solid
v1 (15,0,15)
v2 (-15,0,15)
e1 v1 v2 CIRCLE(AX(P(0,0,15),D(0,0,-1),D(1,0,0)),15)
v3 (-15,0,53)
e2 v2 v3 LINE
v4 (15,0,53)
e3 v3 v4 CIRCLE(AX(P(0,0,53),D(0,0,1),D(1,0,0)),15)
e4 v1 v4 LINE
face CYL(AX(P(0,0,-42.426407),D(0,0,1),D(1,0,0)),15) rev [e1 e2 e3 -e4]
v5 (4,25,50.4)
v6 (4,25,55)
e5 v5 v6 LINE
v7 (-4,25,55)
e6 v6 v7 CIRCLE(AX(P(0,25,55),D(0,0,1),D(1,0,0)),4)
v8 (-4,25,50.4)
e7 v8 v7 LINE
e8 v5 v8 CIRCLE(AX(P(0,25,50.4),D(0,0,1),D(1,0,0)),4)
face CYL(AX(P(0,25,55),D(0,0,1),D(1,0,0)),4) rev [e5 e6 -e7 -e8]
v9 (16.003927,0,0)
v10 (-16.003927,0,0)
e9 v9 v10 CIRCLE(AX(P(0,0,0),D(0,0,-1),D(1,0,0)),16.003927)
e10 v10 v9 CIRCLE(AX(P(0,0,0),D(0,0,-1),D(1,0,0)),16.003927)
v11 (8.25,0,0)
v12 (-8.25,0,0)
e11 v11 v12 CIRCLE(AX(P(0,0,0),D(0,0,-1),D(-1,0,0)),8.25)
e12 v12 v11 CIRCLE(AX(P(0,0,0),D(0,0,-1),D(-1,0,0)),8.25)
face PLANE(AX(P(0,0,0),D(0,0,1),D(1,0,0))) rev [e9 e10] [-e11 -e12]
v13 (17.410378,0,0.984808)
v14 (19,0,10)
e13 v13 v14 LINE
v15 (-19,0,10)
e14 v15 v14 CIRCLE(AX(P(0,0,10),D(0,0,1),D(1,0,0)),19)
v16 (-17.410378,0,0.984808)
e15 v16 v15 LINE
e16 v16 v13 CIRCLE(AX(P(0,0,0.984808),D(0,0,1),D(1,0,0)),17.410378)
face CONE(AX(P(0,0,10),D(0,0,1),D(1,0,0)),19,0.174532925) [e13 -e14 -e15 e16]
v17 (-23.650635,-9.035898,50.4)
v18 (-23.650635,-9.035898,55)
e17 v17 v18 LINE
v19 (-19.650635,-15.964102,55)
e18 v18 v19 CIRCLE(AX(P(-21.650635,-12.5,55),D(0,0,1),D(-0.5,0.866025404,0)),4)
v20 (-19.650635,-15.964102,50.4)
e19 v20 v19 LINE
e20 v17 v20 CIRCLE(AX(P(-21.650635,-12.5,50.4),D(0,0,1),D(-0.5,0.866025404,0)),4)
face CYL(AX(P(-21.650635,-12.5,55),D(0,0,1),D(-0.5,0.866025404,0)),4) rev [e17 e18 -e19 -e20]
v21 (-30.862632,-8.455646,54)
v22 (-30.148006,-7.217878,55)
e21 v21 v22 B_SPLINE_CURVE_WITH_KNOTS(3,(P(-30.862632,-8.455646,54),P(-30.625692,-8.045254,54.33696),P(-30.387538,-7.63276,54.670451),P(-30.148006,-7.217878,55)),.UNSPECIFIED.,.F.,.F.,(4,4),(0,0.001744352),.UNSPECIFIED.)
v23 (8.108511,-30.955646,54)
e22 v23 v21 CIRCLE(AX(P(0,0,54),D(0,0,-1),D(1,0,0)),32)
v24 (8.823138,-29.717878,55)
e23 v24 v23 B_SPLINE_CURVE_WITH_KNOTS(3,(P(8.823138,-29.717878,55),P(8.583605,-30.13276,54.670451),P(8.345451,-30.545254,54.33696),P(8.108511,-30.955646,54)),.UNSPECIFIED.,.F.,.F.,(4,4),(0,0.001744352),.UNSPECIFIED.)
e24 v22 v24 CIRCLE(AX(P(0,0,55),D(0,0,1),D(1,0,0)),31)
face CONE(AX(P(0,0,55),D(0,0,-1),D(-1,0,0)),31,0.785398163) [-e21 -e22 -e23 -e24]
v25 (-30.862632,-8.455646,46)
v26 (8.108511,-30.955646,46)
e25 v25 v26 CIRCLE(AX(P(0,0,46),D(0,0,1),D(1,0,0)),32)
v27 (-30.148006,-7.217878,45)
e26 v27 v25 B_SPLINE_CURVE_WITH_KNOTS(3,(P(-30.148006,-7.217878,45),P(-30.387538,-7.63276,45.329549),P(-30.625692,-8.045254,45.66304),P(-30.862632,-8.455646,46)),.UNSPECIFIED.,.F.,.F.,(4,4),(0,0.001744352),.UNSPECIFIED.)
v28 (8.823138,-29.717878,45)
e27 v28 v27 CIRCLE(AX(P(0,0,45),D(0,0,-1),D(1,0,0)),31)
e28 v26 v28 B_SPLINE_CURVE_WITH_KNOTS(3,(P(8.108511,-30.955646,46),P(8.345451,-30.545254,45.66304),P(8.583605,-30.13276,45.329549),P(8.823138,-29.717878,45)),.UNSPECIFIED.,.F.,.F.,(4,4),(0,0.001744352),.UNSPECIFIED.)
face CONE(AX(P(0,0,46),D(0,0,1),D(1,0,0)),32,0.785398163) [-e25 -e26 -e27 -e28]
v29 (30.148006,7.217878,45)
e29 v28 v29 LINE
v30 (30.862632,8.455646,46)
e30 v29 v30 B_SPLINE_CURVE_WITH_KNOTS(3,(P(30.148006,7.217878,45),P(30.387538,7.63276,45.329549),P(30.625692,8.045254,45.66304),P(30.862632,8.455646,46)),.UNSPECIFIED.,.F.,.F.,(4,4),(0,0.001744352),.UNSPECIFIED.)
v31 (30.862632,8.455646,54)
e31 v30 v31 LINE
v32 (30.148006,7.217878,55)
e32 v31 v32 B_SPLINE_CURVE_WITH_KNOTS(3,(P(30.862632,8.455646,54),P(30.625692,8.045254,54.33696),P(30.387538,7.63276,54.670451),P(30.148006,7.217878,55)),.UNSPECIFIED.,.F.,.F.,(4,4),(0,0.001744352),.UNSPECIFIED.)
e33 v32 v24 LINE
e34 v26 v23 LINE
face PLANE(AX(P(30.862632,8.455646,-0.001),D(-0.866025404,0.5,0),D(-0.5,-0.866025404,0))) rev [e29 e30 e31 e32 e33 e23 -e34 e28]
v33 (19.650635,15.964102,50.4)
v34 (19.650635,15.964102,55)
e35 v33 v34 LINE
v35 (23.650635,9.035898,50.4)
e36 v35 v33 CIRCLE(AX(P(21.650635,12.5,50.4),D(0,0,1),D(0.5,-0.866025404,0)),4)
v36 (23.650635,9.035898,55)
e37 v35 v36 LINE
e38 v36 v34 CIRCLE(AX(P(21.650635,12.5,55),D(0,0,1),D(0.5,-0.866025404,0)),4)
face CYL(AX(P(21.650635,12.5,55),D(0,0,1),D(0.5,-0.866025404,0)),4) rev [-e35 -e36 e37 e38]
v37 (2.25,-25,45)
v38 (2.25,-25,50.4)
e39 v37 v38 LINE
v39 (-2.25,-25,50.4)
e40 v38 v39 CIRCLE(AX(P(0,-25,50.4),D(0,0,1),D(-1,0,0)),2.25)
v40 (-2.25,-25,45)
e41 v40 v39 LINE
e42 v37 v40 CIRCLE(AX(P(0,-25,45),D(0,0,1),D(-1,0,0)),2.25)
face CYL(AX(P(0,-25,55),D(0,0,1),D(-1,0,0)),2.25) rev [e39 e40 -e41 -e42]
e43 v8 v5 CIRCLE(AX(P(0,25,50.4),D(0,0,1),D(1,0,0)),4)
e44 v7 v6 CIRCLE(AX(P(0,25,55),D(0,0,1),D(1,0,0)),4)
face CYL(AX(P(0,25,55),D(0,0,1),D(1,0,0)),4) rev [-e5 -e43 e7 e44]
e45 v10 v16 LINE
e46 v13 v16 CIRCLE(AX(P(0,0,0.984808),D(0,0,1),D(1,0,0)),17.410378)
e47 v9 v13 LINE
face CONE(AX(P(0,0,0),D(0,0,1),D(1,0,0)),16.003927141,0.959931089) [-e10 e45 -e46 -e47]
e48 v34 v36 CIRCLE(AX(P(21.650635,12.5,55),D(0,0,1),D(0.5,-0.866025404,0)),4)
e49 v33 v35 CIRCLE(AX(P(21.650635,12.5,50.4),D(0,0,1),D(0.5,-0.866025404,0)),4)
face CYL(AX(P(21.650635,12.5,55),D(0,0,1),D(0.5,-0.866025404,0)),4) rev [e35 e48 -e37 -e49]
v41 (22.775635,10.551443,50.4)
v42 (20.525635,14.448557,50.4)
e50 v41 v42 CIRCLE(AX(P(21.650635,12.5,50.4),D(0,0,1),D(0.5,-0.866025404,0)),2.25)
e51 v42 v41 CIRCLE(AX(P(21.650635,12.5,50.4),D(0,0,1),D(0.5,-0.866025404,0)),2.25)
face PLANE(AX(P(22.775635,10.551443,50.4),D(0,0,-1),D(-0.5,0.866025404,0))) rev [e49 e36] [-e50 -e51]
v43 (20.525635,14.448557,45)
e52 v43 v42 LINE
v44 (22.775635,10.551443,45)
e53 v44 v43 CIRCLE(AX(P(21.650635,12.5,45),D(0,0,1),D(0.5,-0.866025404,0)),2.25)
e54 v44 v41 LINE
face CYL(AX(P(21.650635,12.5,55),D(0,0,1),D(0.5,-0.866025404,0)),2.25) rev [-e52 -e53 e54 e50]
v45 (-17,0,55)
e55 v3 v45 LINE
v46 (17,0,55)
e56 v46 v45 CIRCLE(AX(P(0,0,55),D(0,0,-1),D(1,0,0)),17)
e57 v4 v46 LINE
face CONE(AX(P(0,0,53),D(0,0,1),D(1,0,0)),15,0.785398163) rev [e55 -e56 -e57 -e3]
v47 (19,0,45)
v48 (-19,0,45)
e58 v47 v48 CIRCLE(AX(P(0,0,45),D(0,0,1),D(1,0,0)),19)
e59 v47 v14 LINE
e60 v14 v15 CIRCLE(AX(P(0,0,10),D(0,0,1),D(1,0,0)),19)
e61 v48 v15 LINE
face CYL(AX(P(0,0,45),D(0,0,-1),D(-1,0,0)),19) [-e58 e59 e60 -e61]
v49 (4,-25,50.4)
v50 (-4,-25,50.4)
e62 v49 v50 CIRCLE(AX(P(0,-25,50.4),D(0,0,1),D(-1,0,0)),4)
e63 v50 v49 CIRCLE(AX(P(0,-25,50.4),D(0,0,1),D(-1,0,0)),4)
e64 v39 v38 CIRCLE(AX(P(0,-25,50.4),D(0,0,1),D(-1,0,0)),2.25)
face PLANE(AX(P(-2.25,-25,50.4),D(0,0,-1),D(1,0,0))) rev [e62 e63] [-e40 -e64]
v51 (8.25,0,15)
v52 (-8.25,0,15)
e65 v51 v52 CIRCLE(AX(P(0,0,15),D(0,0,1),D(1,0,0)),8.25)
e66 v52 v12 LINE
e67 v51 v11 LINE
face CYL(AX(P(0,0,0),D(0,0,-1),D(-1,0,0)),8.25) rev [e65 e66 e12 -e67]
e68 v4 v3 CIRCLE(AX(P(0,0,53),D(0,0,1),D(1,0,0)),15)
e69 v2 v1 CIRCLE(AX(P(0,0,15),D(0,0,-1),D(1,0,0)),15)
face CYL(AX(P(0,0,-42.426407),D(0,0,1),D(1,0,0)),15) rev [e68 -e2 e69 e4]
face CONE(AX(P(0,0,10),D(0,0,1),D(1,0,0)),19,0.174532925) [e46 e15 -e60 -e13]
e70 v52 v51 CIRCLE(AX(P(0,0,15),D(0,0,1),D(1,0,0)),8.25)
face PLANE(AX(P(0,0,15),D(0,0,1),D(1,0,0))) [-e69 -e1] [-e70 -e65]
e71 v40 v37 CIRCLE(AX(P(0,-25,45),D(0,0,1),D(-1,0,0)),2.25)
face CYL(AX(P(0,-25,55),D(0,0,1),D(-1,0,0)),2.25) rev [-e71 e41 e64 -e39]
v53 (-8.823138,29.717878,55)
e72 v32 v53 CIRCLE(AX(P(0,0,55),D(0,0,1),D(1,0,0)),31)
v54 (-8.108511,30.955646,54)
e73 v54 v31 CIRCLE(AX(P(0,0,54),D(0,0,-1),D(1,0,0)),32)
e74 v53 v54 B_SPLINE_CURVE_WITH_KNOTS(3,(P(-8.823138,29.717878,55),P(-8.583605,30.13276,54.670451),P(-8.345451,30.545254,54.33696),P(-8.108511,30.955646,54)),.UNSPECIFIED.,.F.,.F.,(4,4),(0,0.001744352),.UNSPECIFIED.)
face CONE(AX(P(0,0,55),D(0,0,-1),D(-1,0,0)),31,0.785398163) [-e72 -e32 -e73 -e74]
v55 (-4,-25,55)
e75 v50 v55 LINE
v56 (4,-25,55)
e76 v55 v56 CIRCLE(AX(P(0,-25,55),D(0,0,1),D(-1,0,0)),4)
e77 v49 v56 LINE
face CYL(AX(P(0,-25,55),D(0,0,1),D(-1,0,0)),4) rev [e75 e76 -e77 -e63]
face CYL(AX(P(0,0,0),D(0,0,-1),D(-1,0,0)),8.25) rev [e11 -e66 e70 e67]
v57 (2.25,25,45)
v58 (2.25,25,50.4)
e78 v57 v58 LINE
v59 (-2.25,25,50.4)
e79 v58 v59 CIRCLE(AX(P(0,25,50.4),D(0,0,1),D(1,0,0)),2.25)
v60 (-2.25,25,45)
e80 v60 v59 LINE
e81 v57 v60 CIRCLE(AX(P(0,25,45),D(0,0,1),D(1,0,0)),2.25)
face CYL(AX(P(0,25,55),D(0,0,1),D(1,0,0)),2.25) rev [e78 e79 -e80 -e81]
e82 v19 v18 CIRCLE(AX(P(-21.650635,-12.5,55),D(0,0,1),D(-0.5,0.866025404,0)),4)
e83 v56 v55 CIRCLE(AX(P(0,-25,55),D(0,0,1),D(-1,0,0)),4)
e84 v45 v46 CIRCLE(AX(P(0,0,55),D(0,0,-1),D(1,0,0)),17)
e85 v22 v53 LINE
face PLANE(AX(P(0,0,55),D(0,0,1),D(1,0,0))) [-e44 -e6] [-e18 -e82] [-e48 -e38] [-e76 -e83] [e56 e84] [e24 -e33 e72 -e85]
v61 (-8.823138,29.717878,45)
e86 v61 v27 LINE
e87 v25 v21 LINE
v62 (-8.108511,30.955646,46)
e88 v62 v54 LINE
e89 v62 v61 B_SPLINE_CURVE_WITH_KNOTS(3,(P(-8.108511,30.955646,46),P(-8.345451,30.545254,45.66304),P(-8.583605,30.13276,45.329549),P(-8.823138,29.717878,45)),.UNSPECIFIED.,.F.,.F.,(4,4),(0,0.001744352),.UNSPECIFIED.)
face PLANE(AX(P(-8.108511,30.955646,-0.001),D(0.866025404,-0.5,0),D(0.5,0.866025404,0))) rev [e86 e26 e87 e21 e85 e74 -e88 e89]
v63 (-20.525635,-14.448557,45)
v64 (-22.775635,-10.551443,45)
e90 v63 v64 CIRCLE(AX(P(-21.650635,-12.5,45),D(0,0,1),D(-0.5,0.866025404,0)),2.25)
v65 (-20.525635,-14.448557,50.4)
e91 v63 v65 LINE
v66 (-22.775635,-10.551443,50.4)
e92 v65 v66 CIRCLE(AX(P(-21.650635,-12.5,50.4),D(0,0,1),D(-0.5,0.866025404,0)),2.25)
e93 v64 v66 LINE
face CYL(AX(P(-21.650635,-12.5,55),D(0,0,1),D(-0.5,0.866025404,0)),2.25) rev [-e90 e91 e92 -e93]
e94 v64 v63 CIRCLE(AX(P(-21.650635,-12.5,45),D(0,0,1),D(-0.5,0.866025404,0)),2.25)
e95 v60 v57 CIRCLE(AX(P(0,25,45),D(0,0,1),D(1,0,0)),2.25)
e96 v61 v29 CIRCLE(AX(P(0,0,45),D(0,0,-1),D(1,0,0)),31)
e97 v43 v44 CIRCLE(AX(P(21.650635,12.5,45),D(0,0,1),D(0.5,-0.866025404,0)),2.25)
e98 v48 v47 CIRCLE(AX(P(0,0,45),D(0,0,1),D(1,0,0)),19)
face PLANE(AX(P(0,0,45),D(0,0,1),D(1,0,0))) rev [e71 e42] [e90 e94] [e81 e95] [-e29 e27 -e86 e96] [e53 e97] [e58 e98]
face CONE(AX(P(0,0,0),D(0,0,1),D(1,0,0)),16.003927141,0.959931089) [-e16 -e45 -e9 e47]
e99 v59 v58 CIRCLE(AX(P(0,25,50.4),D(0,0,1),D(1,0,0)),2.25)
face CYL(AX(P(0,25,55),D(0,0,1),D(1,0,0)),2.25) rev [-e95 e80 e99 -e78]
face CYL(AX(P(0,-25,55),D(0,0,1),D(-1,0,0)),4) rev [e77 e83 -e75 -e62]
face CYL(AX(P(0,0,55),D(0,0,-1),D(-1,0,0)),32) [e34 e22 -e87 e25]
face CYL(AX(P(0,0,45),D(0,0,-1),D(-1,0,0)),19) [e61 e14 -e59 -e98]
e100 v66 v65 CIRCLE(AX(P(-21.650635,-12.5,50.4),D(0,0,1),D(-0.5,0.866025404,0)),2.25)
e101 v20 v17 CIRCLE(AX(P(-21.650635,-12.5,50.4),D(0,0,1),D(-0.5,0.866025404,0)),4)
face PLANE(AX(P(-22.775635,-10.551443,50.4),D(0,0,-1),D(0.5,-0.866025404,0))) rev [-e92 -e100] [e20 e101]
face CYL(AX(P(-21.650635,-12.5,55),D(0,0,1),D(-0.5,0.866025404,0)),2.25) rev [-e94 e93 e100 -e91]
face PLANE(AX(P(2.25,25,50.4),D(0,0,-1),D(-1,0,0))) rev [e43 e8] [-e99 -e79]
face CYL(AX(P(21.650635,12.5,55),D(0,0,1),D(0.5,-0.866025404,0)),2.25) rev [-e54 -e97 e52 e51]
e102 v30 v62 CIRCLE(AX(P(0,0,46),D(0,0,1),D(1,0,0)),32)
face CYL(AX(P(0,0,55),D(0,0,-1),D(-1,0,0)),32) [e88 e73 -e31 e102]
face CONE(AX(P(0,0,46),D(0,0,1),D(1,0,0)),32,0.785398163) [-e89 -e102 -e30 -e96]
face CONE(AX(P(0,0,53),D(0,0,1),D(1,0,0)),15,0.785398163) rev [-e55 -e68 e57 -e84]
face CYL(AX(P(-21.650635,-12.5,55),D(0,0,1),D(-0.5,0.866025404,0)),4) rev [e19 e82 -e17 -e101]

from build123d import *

# Parameters (mm, degrees)
SKETCH1_R                                            = 19
BOSS_EXTRUDE1_DEPTH                                  = 45
SKETCH2_R                                            = 15
CUT_EXTRUDE1_DEPTH                                   = 30
M18X1_5_TAPPED_HOLE1_D                               = 16.5
M18X1_5_TAPPED_HOLE1_DEPTH                           = 43.5
M18X1_5_TAPPED_HOLE1_TIP                             = 4.957100107
BOSS_EXTRUDE2_START                                  = 10
SKETCH5_R                                            = 32
SKETCH5_R_2                                          = 15
BOSS_EXTRUDE2_DEPTH                                  = 10
HOLE_SIZE_PER_SOCKET_HEAD_CAP_SCREW_TYPE_D           = 4.5
HOLE_SIZE_PER_SOCKET_HEAD_CAP_SCREW_TYPE_CBORE_D     = 8
HOLE_SIZE_PER_SOCKET_HEAD_CAP_SCREW_TYPE_CBORE_DEPTH = 4.6
CIRPATTERN1_COUNT                                    = 6
CUT_EXTRUDE2_REACH                                   = 73.225
CHAMFER1_SIZE                                        = 1
CHAMFER2_SIZE                                        = 10
CHAMFER2_SIZE2                                       = 1.763269807
CHAMFER3_SIZE                                        = 1
CHAMFER3_SIZE2                                       = 1.232803052
CHAMFER4_SIZE                                        = 2


with BuildPart() as part:
    # Sketch1 → Boss-Extrude1 (new body)
    with BuildSketch(Plane.XY):
        with Locations(Location((0, 0, 0), (0, 0, 180))):
            Circle(SKETCH1_R)
    extrude(amount=BOSS_EXTRUDE1_DEPTH)

    # Sketch2 → Cut-Extrude1 (cut)
    with BuildSketch(Plane.XY.offset(45)):
        Circle(SKETCH2_R)
    extrude(amount=-CUT_EXTRUDE1_DEPTH, mode=Mode.SUBTRACT)

    # M18x1.5 Tapped Hole1
    with Locations(Plane(origin=(0, 0, 0), x_dir=(-1, 0, 0), z_dir=(0, 0, -1))):
        with Locations((0, 0)):
            Hole(M18X1_5_TAPPED_HOLE1_D / 2, depth=M18X1_5_TAPPED_HOLE1_DEPTH)
            with Locations((0, 0, -(M18X1_5_TAPPED_HOLE1_DEPTH + M18X1_5_TAPPED_HOLE1_TIP / 2))):  # 118° drill point
                Cone(0, M18X1_5_TAPPED_HOLE1_D / 2, M18X1_5_TAPPED_HOLE1_TIP, mode=Mode.SUBTRACT)

    # Sketch5 → Boss-Extrude2 (add)
    with BuildSketch(Plane.XY.offset(45).offset(BOSS_EXTRUDE2_START)):
        Circle(SKETCH5_R)
        Circle(SKETCH5_R_2, mode=Mode.SUBTRACT)
    extrude(amount=-BOSS_EXTRUDE2_DEPTH)

    # Hole size per socket head cap screw type1 (through all)
    with Locations(Plane(origin=(0, 25, 55), x_dir=(1, 0, 0), z_dir=(0, 0, 1))):
        with Locations((0, 0)):
            hole_size_per_socket_head_cap_screw_type = CounterBoreHole(HOLE_SIZE_PER_SOCKET_HEAD_CAP_SCREW_TYPE_D / 2, HOLE_SIZE_PER_SOCKET_HEAD_CAP_SCREW_TYPE_CBORE_D / 2, HOLE_SIZE_PER_SOCKET_HEAD_CAP_SCREW_TYPE_CBORE_DEPTH)

    # CirPattern1: Hole size per socket head cap screw type1 ×6 about axis, 2 skipped
    cirpattern1_axis = Axis((0, 0, 55), (0, 0, 1))
    add([hole_size_per_socket_head_cap_screw_type.rotate(cirpattern1_axis, i * 360 / CIRPATTERN1_COUNT) for i in range(1, CIRPATTERN1_COUNT) if i not in (1, 4)], mode=Mode.SUBTRACT)

    # Sketch7 → Cut-Extrude2 (cut, up to next)
    with BuildSketch(Plane.XY.offset(55), mode=Mode.PRIVATE) as cut_extrude2_sk1:
        with BuildLine():
            Line((-8.108511332, 30.955646399), (-30.862631838, -8.455646399))
            ThreePointArc((-30.862631838, -8.455646399), (-27.712812921, 16), (-8.108511332, 30.955646399))
        make_face()
    cut_extrude2_tool1 = extrude(cut_extrude2_sk1.sketch, amount=-CUT_EXTRUDE2_REACH, mode=Mode.PRIVATE) & part.part
    # Sketch7 → Cut-Extrude2 (cut, up to next)
    with BuildSketch(Plane.XY.offset(55), mode=Mode.PRIVATE) as cut_extrude2_sk2:
        with BuildLine():
            Line((30.862631838, 8.455646399), (8.108511332, -30.955646399))
            ThreePointArc((8.108511332, -30.955646399), (27.712812921, -16), (30.862631838, 8.455646399))
        make_face()
    cut_extrude2_tool2 = extrude(cut_extrude2_sk2.sketch, amount=-CUT_EXTRUDE2_REACH, mode=Mode.PRIVATE) & part.part
    add(cut_extrude2_tool1.solids().sort_by_distance((-22.822298, 13.17646, 55))[0], mode=Mode.SUBTRACT)
    add(cut_extrude2_tool2.solids().sort_by_distance((22.822298, -13.17646, 55))[0], mode=Mode.SUBTRACT)

    # Chamfer1
    chamfer1_edges = [part.edges().sort_by_distance(p)[0] for p in [
        (-16, -27.712812921, 55),
        (-16, -27.712812921, 45),
        (16, 27.712812921, 55),
        (16, 27.712812921, 45),
    ]]
    chamfer(chamfer1_edges, length=CHAMFER1_SIZE)

    # Chamfer2
    chamfer2_edges = [part.edges().sort_by_distance(p)[0] for p in [
        (19, 0, 0),
    ]]
    chamfer2_side = [part.faces().sort_by_distance(p)[0] for p in [
        (19, 0, 22.5),
    ]]
    chamfer(chamfer2_edges, length=CHAMFER2_SIZE, length2=CHAMFER2_SIZE2, reference=chamfer2_side[0])

    # Chamfer3
    chamfer3_edges = [part.edges().sort_by_distance(p)[0] for p in [
        (17.236730193, 0, 0),
    ]]
    chamfer3_side = [part.faces().sort_by_distance(p)[0] for p in [
        (18.118365096, 0, 5),
    ]]
    chamfer(chamfer3_edges, length=CHAMFER3_SIZE, length2=CHAMFER3_SIZE2, reference=chamfer3_side[0])

    # Chamfer4
    chamfer4_edges = [part.edges().sort_by_distance(p)[0] for p in [
        (-15, 0, 55),
    ]]
    chamfer(chamfer4_edges, length=CHAMFER4_SIZE)


solid = part.part
